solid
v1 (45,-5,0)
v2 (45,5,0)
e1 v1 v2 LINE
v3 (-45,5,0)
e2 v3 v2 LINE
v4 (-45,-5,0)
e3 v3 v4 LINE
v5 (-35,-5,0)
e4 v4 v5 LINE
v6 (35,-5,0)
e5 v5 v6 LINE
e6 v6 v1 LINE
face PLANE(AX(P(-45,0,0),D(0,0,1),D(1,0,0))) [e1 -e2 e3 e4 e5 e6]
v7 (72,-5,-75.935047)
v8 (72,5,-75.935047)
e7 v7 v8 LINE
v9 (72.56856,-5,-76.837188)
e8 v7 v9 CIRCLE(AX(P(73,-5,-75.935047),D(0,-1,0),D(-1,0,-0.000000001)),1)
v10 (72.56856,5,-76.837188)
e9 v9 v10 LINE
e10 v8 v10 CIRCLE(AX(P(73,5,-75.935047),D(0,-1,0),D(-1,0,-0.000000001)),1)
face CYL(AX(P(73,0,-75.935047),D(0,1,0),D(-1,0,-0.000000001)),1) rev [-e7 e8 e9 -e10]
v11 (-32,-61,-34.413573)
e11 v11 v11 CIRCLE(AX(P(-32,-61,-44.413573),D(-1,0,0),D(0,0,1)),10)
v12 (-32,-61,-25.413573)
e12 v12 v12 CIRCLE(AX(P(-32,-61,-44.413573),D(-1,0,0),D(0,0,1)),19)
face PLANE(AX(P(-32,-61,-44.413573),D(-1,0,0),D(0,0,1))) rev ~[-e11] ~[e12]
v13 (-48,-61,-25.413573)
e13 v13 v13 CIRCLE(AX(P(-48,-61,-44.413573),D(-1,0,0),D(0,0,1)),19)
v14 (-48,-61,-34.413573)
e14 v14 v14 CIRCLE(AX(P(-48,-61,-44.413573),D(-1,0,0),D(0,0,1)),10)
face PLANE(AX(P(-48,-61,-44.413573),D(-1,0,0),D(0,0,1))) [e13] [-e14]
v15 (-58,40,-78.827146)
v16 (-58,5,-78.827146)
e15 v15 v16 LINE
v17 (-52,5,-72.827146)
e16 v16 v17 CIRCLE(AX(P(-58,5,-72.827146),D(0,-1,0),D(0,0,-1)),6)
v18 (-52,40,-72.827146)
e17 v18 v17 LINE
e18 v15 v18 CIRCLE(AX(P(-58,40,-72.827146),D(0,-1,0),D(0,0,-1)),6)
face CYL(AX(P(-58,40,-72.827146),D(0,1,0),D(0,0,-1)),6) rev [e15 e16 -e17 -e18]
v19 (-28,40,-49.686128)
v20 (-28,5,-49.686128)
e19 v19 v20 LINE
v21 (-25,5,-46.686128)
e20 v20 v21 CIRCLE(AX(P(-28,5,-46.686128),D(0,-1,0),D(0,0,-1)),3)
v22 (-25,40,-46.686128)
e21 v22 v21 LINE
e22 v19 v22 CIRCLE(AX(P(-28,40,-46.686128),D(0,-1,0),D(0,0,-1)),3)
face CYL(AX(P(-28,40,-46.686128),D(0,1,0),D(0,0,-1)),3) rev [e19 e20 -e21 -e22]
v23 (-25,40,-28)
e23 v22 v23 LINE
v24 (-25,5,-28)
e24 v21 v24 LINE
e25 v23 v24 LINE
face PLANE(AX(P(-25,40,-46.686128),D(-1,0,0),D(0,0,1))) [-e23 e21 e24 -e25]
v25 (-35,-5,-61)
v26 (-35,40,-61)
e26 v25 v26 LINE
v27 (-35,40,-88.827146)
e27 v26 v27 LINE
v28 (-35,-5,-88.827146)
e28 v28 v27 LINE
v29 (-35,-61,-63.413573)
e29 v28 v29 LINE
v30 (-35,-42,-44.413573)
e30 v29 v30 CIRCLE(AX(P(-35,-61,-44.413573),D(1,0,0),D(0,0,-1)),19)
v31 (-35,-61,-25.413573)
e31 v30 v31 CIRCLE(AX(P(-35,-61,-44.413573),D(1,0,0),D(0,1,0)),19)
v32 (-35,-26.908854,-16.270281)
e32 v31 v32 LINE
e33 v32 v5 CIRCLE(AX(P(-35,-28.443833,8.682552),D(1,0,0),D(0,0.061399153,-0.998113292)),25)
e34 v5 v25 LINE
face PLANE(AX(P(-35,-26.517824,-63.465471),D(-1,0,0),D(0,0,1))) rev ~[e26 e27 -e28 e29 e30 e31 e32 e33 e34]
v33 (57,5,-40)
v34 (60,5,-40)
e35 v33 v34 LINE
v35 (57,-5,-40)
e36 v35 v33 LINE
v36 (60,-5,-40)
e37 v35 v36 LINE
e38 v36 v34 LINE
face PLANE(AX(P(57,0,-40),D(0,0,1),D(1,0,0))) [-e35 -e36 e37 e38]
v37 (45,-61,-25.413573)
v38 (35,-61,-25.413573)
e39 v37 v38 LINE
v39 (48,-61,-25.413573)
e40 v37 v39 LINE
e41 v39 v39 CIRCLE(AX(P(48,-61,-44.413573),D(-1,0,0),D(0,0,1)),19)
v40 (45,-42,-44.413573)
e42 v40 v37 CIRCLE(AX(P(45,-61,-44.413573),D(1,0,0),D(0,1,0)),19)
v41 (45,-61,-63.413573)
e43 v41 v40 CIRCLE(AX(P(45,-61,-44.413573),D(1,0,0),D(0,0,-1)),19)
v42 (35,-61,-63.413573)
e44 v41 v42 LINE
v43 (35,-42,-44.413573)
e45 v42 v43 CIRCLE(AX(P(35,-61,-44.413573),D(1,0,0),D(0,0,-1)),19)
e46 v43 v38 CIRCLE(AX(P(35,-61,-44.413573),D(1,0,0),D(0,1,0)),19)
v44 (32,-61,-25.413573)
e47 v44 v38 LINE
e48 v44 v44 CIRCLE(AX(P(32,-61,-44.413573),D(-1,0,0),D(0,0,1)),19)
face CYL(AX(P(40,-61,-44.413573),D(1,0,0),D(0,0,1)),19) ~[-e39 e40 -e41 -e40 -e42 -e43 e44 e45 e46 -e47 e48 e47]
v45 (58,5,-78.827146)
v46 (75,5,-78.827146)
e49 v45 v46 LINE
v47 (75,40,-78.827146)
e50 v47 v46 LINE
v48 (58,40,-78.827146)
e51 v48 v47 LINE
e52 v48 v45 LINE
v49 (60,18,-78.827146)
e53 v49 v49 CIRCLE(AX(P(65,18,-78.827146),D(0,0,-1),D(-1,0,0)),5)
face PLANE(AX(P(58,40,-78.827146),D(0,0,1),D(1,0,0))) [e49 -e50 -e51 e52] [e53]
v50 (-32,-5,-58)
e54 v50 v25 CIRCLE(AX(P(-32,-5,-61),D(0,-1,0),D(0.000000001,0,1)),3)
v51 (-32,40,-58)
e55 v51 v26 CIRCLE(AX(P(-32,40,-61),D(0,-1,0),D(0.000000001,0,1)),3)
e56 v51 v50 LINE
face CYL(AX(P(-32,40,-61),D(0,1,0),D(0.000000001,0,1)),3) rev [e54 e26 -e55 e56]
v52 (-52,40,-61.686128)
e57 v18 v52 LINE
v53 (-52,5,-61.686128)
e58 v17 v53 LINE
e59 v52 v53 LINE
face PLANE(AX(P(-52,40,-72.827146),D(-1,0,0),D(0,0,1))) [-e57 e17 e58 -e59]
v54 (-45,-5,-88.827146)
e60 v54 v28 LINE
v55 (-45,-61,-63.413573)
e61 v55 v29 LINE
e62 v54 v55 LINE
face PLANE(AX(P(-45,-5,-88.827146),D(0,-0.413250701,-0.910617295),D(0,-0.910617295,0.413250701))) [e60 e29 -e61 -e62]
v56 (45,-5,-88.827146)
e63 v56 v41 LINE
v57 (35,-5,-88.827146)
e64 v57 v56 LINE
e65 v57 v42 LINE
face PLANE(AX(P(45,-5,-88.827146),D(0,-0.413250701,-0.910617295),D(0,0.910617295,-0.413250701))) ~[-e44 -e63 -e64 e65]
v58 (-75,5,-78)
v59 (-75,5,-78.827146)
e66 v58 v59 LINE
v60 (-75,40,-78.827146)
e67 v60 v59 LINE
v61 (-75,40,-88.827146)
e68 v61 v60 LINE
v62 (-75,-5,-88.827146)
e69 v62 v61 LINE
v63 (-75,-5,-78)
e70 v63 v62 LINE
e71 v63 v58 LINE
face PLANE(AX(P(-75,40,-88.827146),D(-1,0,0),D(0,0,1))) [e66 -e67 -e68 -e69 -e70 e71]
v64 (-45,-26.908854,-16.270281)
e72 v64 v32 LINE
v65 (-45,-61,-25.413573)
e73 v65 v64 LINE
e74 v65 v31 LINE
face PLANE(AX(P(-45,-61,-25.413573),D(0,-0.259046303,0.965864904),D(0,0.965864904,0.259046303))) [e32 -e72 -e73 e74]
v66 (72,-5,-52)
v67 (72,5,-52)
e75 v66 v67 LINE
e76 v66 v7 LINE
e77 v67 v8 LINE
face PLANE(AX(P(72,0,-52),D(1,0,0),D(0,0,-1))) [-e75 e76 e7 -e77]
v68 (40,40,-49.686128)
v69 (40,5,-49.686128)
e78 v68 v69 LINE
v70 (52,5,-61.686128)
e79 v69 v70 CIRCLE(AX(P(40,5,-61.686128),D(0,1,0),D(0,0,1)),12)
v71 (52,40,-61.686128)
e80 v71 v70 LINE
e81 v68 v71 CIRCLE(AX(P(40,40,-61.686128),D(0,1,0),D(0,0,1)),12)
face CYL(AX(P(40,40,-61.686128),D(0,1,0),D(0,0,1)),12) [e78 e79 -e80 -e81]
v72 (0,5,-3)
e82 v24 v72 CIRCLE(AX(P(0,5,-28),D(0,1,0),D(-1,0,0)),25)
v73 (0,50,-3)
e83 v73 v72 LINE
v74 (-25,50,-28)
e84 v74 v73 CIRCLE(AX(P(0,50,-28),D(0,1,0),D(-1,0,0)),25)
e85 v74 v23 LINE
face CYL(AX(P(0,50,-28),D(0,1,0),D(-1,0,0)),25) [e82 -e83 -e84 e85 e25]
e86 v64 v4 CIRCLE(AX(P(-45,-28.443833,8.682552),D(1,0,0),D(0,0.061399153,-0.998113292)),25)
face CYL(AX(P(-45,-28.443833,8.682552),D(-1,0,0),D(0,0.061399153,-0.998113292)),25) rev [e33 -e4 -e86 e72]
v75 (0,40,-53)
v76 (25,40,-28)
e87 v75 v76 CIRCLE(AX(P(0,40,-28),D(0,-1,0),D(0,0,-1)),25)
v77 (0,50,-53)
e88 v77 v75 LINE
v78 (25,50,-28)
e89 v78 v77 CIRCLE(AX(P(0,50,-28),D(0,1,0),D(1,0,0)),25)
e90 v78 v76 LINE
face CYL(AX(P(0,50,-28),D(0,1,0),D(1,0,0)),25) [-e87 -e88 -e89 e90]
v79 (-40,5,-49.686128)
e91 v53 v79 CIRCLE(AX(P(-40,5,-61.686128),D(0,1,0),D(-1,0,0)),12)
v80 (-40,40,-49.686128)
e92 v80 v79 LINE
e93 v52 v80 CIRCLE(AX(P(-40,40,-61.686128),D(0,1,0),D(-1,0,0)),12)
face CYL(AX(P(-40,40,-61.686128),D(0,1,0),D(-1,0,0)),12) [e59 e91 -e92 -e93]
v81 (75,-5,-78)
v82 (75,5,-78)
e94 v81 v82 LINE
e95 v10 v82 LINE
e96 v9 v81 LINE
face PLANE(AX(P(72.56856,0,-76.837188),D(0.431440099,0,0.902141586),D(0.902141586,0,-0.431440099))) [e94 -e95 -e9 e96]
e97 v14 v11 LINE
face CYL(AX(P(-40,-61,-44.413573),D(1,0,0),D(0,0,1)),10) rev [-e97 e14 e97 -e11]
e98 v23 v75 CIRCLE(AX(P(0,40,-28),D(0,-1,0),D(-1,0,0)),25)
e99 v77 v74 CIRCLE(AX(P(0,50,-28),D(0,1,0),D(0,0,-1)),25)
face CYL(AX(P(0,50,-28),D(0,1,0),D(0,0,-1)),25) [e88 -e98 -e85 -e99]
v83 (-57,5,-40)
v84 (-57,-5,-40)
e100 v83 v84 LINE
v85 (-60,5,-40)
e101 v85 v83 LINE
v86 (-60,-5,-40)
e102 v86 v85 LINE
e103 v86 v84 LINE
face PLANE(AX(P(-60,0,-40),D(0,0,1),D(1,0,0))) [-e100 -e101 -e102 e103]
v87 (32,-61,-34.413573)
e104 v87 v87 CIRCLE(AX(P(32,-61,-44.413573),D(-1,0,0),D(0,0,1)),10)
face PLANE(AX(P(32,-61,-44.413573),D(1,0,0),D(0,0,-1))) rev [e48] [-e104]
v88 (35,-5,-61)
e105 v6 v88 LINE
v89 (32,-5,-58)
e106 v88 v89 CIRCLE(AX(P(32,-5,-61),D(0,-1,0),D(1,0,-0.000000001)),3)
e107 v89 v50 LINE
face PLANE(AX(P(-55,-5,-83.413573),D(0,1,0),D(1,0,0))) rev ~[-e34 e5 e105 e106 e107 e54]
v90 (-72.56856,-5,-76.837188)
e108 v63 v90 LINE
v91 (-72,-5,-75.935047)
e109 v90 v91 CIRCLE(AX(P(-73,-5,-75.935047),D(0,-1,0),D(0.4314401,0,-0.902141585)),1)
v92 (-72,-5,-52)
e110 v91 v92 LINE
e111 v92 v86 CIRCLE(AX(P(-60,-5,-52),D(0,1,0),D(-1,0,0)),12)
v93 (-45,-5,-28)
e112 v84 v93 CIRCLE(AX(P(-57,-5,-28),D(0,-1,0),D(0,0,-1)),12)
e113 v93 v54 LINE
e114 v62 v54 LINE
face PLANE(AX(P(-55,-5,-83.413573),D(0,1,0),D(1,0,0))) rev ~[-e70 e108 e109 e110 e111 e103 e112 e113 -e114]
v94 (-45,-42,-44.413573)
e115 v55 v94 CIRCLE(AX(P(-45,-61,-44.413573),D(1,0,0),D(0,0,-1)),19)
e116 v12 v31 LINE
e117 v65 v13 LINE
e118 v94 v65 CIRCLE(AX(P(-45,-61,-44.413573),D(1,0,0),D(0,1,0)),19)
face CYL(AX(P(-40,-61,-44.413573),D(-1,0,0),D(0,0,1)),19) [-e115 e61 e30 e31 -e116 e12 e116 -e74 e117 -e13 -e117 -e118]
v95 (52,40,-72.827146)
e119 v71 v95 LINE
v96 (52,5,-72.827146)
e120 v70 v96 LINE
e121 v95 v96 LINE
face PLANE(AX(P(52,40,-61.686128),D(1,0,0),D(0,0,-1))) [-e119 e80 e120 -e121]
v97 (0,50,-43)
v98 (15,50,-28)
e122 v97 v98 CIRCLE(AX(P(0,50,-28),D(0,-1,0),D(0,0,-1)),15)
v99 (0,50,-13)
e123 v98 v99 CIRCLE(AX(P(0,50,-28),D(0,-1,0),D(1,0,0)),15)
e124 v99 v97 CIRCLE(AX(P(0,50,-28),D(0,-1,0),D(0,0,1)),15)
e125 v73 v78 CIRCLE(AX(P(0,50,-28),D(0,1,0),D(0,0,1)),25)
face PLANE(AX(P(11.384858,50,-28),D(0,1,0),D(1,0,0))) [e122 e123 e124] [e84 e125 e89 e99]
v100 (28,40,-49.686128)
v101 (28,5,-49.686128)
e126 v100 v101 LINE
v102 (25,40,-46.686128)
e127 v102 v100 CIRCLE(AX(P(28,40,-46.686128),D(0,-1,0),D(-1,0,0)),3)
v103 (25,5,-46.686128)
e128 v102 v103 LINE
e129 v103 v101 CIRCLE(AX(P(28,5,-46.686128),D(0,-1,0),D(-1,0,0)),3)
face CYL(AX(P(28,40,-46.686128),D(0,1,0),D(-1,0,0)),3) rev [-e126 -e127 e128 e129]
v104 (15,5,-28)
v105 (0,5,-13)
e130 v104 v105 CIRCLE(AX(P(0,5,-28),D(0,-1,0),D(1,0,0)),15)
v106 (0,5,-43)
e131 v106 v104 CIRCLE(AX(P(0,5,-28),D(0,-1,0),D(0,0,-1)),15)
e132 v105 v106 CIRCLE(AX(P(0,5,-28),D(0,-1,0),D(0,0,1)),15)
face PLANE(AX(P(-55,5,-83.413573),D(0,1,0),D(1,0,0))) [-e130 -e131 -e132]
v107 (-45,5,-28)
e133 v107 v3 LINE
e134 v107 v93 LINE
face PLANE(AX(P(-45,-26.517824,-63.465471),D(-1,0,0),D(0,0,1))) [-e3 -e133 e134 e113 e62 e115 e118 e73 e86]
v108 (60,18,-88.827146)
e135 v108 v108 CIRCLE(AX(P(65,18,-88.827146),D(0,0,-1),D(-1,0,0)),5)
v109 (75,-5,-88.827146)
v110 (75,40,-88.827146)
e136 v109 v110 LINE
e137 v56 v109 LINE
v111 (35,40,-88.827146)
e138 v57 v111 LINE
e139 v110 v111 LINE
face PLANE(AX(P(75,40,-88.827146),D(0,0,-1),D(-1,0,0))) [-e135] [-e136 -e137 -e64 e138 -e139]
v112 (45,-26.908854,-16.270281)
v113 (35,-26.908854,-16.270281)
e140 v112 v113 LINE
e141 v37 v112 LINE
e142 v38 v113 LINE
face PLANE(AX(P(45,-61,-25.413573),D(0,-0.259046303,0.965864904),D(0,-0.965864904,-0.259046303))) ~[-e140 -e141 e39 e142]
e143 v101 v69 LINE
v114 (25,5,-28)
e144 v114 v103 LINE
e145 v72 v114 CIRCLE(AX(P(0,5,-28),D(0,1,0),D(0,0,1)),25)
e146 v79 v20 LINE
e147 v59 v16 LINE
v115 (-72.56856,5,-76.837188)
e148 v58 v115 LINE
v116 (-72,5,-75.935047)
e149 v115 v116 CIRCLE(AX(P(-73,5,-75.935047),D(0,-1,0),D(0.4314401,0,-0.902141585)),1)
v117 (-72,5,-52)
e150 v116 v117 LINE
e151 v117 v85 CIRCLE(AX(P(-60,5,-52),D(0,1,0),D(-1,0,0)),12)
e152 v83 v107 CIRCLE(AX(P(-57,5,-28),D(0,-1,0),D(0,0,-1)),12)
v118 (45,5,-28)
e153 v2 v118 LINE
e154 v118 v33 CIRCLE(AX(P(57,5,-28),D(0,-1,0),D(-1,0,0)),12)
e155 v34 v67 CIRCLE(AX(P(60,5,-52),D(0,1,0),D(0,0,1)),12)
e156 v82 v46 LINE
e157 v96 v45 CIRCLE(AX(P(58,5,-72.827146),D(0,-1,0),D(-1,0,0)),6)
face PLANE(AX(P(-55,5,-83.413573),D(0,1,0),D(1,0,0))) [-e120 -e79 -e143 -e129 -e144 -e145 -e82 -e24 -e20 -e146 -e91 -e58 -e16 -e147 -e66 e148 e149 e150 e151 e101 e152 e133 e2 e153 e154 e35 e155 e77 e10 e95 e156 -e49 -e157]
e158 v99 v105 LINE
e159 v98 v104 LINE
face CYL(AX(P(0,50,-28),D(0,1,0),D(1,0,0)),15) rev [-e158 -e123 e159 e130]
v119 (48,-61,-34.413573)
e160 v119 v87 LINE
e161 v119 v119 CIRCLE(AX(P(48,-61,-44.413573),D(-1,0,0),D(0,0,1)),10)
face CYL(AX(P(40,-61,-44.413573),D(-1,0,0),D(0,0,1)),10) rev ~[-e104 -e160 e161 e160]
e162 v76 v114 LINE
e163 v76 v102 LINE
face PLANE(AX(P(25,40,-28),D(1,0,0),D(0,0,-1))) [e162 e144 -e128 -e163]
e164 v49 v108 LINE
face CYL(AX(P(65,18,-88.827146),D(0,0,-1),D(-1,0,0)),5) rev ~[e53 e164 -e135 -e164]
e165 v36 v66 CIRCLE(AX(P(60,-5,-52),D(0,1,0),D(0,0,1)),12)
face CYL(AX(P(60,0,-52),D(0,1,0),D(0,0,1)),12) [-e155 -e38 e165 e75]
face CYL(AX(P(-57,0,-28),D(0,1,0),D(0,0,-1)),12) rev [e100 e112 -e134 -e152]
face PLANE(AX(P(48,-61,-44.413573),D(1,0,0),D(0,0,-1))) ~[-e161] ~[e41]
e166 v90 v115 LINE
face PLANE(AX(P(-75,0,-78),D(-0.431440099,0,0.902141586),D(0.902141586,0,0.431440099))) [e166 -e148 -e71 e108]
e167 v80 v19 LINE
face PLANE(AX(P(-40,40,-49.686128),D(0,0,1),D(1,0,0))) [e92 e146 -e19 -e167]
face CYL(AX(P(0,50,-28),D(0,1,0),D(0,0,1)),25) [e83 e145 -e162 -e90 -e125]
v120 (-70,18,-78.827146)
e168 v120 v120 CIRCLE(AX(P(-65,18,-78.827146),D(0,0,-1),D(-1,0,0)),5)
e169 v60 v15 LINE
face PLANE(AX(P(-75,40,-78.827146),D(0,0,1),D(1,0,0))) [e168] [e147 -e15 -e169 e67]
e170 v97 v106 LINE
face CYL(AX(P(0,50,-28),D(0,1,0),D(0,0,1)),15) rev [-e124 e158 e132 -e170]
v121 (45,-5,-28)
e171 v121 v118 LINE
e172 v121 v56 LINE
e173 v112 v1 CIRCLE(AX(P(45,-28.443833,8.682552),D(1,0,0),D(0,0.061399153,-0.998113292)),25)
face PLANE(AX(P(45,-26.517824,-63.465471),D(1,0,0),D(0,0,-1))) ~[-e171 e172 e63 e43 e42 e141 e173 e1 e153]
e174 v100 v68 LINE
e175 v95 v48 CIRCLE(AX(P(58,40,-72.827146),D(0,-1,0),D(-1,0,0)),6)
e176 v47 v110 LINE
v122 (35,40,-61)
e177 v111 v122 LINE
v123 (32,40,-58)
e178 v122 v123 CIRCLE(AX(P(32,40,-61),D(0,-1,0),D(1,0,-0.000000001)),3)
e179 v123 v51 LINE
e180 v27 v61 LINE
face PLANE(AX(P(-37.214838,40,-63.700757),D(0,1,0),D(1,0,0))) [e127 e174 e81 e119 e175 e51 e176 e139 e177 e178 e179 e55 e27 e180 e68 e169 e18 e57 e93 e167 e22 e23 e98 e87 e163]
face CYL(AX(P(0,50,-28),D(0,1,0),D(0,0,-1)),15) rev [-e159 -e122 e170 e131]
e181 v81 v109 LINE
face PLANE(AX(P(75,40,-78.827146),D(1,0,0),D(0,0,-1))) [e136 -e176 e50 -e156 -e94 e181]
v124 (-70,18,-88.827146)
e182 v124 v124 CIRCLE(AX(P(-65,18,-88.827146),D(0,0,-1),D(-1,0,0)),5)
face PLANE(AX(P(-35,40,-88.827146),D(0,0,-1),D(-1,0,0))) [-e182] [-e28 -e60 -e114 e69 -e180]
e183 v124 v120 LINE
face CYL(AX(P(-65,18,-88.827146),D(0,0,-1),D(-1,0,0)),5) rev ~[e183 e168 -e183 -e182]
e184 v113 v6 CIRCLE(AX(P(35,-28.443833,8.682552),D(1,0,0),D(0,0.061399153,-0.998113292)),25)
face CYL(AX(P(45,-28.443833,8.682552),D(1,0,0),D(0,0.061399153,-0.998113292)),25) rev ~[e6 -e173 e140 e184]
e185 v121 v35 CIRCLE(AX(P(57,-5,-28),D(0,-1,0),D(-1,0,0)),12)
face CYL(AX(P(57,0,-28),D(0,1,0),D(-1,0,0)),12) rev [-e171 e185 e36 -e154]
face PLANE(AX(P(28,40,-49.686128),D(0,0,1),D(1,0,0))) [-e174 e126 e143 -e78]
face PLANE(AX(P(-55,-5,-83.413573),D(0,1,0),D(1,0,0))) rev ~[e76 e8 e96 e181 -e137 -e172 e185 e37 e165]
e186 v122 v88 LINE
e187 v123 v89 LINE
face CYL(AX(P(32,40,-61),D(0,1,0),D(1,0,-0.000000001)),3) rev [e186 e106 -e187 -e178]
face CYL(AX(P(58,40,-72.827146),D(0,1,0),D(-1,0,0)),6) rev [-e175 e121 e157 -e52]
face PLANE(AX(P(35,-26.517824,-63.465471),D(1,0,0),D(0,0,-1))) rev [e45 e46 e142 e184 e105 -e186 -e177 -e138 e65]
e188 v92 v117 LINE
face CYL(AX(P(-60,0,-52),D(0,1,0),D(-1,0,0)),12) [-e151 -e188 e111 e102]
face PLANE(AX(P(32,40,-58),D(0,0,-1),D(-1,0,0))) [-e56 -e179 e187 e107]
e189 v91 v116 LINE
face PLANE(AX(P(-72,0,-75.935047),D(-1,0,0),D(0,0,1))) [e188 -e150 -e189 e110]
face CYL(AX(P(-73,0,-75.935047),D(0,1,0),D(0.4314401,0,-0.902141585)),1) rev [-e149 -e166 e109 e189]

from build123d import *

# Parameters (mm, degrees)
BASE_PLATE_DEPTH        = 5
RISER_BLOCK_SKETCH_W    = 40
RISER_BLOCK_SKETCH_H    = 10.827146282
RISER_BLOCK_DEPTH       = 10
UPRIGHT_START           = 35
UPRIGHT_BOSS_35MM_DEPTH = 35
UPRIGHT_START_2         = 45
UPRIGHT_BOSS_45MM_DEPTH = 45
BORE_SKETCH_R           = 5
BORE_CUT_DEPTH          = 22.5
MOUNTING_LUG_DEPTH      = 10
LUG_BOSS_SKETCH_R       = 19
LUG_BOSS_SKETCH_R_2     = 10
LUG_BOSS_DEPTH          = 8


with BuildPart() as part:
    # Base Plate Sketch → Base Plate (new, symmetric)
    with BuildSketch(Plane(origin=(0, 0, 0), x_dir=(1, 0, 0), z_dir=(0, 1, 0))):
        with BuildLine():
            Line((-45, 0), (45, 0))
            Line((45, 0), (45, 28))
            ThreePointArc((45, 28), (48.514718626, 36.485281374), (57, 40))
            Line((57, 40), (60, 40))
            ThreePointArc((60, 40), (68.485281374, 43.514718626), (72, 52))
            Line((72, 52), (72, 75.935046753))
            ThreePointArc((72, 75.935046753), (72.153997607, 76.468225851), (72.568559901, 76.837188339))
            Line((72.568559901, 76.837188339), (75, 78))
            Line((75, 78), (72, 78))
            Line((72, 78), (35, 78))
            Line((35, 78), (35, 61))
            ThreePointArc((35, 61), (34.121320344, 58.878679656), (32, 58))
            Line((32, 58), (-32, 58))
            ThreePointArc((-32, 58), (-34.121320344, 58.878679656), (-35, 61))
            Line((-35, 61), (-35, 78))
            Line((-35, 78), (-72, 78))
            Line((-72, 78), (-75, 78))
            Line((-75, 78), (-72.568559901, 76.837188339))
            ThreePointArc((-72.568559901, 76.837188339), (-72.153997607, 76.468225851), (-72, 75.935046753))
            Line((-72, 75.935046753), (-72, 52))
            ThreePointArc((-72, 52), (-68.485281374, 43.514718626), (-60, 40))
            Line((-60, 40), (-57, 40))
            ThreePointArc((-57, 40), (-48.514718626, 36.485281374), (-45, 28))
            Line((-45, 28), (-45, 0))
        make_face()
    extrude(amount=BASE_PLATE_DEPTH, both=True)

    # Riser Block Sketch → Riser Block (add)
    with BuildSketch(Plane(origin=(0, 5, 0), x_dir=(1, 0, 0), z_dir=(0, 1, 0))):
        with Locations((-55, 83.413573141)):
            Rectangle(RISER_BLOCK_SKETCH_W, RISER_BLOCK_SKETCH_H)
        with Locations((55, 83.413573141)):
            Rectangle(RISER_BLOCK_SKETCH_W, RISER_BLOCK_SKETCH_H)
    extrude(amount=-RISER_BLOCK_DEPTH)

    # Upright Bosses Sketch → Upright Boss 35mm (add)
    with BuildSketch(Plane(origin=(0, 5, 0), x_dir=(1, 0, 0), z_dir=(0, 1, 0)).offset(UPRIGHT_START)):
        with BuildLine():
            Line((0, 53), (0, 58))
            Line((0, 58), (-32, 58))
            ThreePointArc((-32, 58), (-34.121320344, 58.878679656), (-35, 61))
            Line((-35, 61), (-35, 88.827146282))
            Line((-35, 88.827146282), (-75, 88.827146282))
            Line((-75, 88.827146282), (-75, 78.827146282))
            Line((-75, 78.827146282), (-58, 78.827146282))
            ThreePointArc((-58, 78.827146282), (-53.757359313, 77.069786969), (-52, 72.827146282))
            Line((-52, 72.827146282), (-52, 61.686127822))
            ThreePointArc((-52, 61.686127822), (-48.485281374, 53.200846447), (-40, 49.686127822))
            Line((-40, 49.686127822), (-28, 49.686127822))
            ThreePointArc((-28, 49.686127822), (-25.878679656, 48.807448165), (-25, 46.686127822))
            Line((-25, 46.686127822), (-25, 28))
            ThreePointArc((-25, 28), (-17.67766953, 45.67766953), (0, 53))
        make_face()
        with BuildLine():
            Line((75, 78.827146282), (75, 88.827146282))
            Line((75, 88.827146282), (35, 88.827146282))
            Line((35, 88.827146282), (35, 61))
            ThreePointArc((35, 61), (34.121320344, 58.878679656), (32, 58))
            Line((32, 58), (0, 58))
            Line((0, 58), (0, 53))
            ThreePointArc((0, 53), (17.67766953, 45.67766953), (25, 28))
            Line((25, 28), (25, 46.686127822))
            ThreePointArc((25, 46.686127822), (25.878679656, 48.807448165), (28, 49.686127822))
            Line((28, 49.686127822), (40, 49.686127822))
            ThreePointArc((40, 49.686127822), (48.485281374, 53.200846447), (52, 61.686127822))
            Line((52, 61.686127822), (52, 72.827146282))
            ThreePointArc((52, 72.827146282), (53.757359313, 77.069786969), (58, 78.827146282))
            Line((58, 78.827146282), (75, 78.827146282))
        make_face()
    extrude(amount=-UPRIGHT_BOSS_35MM_DEPTH)

    # Sketch5_3 → Upright Boss 45mm (add)
    with BuildSketch(Plane(origin=(0, 5, 0), x_dir=(1, 0, 0), z_dir=(0, 1, 0)).offset(UPRIGHT_START_2)):
        with BuildLine():
            ThreePointArc((25, 28), (17.67766953, 45.67766953), (0, 53))
            Line((0, 53), (0, 43))
            ThreePointArc((0, 43), (10.606601718, 38.606601718), (15, 28))
            ThreePointArc((15, 28), (10.606601718, 17.393398282), (0, 13))
            Line((0, 13), (0, 3))
            ThreePointArc((0, 3), (17.67766953, 10.32233047), (25, 28))
        make_face()
        with BuildLine():
            Line((0, 43), (0, 53))
            ThreePointArc((0, 53), (-17.67766953, 45.67766953), (-25, 28))
            ThreePointArc((-25, 28), (-17.67766953, 10.32233047), (0, 3))
            Line((0, 3), (0, 13))
            ThreePointArc((0, 13), (-15, 28), (0, 43))
        make_face()
        with BuildLine():
            ThreePointArc((25, 28), (17.67766953, 45.67766953), (0, 53))
            Line((0, 53), (0, 43))
            ThreePointArc((0, 43), (10.606601718, 38.606601718), (15, 28))
            ThreePointArc((15, 28), (10.606601718, 17.393398282), (0, 13))
            Line((0, 13), (0, 3))
            ThreePointArc((0, 3), (17.67766953, 10.32233047), (25, 28))
        make_face()
        with BuildLine():
            Line((0, 43), (0, 53))
            ThreePointArc((0, 53), (-17.67766953, 45.67766953), (-25, 28))
            ThreePointArc((-25, 28), (-17.67766953, 10.32233047), (0, 3))
            Line((0, 3), (0, 13))
            ThreePointArc((0, 13), (-15, 28), (0, 43))
        make_face()
    extrude(amount=-UPRIGHT_BOSS_45MM_DEPTH)

    # Bore Sketch → Bore Cut (cut, symmetric)
    with BuildSketch(Plane(origin=(0, 0, -88.827146282), x_dir=(-1, 0, 0), z_dir=(0, 0, -1))):
        with Locations((65, 18)):
            Circle(BORE_SKETCH_R)
        with Locations((-65, 18)):
            Circle(BORE_SKETCH_R)
    extrude(amount=BORE_CUT_DEPTH, both=True, mode=Mode.SUBTRACT)

    # Mounting Lug Sketch → Mounting Lug (add)
    with BuildSketch(Plane.ZY.offset(45)):
        with BuildLine():
            Line((-44.413573141, -5), (-88.827146282, -5))
            Line((-88.827146282, -5), (-63.413573141, -61))
            ThreePointArc((-63.413573141, -61), (-57.848601984, -47.564971157), (-44.413573141, -42))
            Line((-44.413573141, -42), (-44.413573141, -5))
        make_face()
        with BuildLine():
            Line((-28, -5), (-44.413573141, -5))
            Line((-44.413573141, -5), (-44.413573141, -42))
            ThreePointArc((-44.413573141, -42), (-30.978544299, -47.564971157), (-25.413573141, -61))
            Line((-25.413573141, -61), (-16.270280631, -26.90885398))
            ThreePointArc((-16.270280631, -26.90885398), (-11.388179119, -13.538606689), (0, -5))
            Line((0, -5), (-28, -5))
        make_face()
    mounting_lug = extrude(amount=-MOUNTING_LUG_DEPTH)

    # Lug Boss Sketch → Lug Boss (add, symmetric)
    with BuildSketch(Plane.ZY.offset(40)):
        with Locations((-44.413573141, -61)):
            Circle(LUG_BOSS_SKETCH_R)
        with Locations((-44.413573141, -61)):
            Circle(LUG_BOSS_SKETCH_R_2, mode=Mode.SUBTRACT)
    lug_boss = extrude(amount=LUG_BOSS_DEPTH, both=True)

    # Lug Mirror: Mounting Lug, Lug Boss across plane
    add(mounting_lug.mirror(Plane(origin=(0, 0, 0), x_dir=(0, 0, 1), z_dir=(1, 0, 0))))
    add(lug_boss.mirror(Plane(origin=(0, 0, 0), x_dir=(0, 0, 1), z_dir=(1, 0, 0))))


solid = part.part
